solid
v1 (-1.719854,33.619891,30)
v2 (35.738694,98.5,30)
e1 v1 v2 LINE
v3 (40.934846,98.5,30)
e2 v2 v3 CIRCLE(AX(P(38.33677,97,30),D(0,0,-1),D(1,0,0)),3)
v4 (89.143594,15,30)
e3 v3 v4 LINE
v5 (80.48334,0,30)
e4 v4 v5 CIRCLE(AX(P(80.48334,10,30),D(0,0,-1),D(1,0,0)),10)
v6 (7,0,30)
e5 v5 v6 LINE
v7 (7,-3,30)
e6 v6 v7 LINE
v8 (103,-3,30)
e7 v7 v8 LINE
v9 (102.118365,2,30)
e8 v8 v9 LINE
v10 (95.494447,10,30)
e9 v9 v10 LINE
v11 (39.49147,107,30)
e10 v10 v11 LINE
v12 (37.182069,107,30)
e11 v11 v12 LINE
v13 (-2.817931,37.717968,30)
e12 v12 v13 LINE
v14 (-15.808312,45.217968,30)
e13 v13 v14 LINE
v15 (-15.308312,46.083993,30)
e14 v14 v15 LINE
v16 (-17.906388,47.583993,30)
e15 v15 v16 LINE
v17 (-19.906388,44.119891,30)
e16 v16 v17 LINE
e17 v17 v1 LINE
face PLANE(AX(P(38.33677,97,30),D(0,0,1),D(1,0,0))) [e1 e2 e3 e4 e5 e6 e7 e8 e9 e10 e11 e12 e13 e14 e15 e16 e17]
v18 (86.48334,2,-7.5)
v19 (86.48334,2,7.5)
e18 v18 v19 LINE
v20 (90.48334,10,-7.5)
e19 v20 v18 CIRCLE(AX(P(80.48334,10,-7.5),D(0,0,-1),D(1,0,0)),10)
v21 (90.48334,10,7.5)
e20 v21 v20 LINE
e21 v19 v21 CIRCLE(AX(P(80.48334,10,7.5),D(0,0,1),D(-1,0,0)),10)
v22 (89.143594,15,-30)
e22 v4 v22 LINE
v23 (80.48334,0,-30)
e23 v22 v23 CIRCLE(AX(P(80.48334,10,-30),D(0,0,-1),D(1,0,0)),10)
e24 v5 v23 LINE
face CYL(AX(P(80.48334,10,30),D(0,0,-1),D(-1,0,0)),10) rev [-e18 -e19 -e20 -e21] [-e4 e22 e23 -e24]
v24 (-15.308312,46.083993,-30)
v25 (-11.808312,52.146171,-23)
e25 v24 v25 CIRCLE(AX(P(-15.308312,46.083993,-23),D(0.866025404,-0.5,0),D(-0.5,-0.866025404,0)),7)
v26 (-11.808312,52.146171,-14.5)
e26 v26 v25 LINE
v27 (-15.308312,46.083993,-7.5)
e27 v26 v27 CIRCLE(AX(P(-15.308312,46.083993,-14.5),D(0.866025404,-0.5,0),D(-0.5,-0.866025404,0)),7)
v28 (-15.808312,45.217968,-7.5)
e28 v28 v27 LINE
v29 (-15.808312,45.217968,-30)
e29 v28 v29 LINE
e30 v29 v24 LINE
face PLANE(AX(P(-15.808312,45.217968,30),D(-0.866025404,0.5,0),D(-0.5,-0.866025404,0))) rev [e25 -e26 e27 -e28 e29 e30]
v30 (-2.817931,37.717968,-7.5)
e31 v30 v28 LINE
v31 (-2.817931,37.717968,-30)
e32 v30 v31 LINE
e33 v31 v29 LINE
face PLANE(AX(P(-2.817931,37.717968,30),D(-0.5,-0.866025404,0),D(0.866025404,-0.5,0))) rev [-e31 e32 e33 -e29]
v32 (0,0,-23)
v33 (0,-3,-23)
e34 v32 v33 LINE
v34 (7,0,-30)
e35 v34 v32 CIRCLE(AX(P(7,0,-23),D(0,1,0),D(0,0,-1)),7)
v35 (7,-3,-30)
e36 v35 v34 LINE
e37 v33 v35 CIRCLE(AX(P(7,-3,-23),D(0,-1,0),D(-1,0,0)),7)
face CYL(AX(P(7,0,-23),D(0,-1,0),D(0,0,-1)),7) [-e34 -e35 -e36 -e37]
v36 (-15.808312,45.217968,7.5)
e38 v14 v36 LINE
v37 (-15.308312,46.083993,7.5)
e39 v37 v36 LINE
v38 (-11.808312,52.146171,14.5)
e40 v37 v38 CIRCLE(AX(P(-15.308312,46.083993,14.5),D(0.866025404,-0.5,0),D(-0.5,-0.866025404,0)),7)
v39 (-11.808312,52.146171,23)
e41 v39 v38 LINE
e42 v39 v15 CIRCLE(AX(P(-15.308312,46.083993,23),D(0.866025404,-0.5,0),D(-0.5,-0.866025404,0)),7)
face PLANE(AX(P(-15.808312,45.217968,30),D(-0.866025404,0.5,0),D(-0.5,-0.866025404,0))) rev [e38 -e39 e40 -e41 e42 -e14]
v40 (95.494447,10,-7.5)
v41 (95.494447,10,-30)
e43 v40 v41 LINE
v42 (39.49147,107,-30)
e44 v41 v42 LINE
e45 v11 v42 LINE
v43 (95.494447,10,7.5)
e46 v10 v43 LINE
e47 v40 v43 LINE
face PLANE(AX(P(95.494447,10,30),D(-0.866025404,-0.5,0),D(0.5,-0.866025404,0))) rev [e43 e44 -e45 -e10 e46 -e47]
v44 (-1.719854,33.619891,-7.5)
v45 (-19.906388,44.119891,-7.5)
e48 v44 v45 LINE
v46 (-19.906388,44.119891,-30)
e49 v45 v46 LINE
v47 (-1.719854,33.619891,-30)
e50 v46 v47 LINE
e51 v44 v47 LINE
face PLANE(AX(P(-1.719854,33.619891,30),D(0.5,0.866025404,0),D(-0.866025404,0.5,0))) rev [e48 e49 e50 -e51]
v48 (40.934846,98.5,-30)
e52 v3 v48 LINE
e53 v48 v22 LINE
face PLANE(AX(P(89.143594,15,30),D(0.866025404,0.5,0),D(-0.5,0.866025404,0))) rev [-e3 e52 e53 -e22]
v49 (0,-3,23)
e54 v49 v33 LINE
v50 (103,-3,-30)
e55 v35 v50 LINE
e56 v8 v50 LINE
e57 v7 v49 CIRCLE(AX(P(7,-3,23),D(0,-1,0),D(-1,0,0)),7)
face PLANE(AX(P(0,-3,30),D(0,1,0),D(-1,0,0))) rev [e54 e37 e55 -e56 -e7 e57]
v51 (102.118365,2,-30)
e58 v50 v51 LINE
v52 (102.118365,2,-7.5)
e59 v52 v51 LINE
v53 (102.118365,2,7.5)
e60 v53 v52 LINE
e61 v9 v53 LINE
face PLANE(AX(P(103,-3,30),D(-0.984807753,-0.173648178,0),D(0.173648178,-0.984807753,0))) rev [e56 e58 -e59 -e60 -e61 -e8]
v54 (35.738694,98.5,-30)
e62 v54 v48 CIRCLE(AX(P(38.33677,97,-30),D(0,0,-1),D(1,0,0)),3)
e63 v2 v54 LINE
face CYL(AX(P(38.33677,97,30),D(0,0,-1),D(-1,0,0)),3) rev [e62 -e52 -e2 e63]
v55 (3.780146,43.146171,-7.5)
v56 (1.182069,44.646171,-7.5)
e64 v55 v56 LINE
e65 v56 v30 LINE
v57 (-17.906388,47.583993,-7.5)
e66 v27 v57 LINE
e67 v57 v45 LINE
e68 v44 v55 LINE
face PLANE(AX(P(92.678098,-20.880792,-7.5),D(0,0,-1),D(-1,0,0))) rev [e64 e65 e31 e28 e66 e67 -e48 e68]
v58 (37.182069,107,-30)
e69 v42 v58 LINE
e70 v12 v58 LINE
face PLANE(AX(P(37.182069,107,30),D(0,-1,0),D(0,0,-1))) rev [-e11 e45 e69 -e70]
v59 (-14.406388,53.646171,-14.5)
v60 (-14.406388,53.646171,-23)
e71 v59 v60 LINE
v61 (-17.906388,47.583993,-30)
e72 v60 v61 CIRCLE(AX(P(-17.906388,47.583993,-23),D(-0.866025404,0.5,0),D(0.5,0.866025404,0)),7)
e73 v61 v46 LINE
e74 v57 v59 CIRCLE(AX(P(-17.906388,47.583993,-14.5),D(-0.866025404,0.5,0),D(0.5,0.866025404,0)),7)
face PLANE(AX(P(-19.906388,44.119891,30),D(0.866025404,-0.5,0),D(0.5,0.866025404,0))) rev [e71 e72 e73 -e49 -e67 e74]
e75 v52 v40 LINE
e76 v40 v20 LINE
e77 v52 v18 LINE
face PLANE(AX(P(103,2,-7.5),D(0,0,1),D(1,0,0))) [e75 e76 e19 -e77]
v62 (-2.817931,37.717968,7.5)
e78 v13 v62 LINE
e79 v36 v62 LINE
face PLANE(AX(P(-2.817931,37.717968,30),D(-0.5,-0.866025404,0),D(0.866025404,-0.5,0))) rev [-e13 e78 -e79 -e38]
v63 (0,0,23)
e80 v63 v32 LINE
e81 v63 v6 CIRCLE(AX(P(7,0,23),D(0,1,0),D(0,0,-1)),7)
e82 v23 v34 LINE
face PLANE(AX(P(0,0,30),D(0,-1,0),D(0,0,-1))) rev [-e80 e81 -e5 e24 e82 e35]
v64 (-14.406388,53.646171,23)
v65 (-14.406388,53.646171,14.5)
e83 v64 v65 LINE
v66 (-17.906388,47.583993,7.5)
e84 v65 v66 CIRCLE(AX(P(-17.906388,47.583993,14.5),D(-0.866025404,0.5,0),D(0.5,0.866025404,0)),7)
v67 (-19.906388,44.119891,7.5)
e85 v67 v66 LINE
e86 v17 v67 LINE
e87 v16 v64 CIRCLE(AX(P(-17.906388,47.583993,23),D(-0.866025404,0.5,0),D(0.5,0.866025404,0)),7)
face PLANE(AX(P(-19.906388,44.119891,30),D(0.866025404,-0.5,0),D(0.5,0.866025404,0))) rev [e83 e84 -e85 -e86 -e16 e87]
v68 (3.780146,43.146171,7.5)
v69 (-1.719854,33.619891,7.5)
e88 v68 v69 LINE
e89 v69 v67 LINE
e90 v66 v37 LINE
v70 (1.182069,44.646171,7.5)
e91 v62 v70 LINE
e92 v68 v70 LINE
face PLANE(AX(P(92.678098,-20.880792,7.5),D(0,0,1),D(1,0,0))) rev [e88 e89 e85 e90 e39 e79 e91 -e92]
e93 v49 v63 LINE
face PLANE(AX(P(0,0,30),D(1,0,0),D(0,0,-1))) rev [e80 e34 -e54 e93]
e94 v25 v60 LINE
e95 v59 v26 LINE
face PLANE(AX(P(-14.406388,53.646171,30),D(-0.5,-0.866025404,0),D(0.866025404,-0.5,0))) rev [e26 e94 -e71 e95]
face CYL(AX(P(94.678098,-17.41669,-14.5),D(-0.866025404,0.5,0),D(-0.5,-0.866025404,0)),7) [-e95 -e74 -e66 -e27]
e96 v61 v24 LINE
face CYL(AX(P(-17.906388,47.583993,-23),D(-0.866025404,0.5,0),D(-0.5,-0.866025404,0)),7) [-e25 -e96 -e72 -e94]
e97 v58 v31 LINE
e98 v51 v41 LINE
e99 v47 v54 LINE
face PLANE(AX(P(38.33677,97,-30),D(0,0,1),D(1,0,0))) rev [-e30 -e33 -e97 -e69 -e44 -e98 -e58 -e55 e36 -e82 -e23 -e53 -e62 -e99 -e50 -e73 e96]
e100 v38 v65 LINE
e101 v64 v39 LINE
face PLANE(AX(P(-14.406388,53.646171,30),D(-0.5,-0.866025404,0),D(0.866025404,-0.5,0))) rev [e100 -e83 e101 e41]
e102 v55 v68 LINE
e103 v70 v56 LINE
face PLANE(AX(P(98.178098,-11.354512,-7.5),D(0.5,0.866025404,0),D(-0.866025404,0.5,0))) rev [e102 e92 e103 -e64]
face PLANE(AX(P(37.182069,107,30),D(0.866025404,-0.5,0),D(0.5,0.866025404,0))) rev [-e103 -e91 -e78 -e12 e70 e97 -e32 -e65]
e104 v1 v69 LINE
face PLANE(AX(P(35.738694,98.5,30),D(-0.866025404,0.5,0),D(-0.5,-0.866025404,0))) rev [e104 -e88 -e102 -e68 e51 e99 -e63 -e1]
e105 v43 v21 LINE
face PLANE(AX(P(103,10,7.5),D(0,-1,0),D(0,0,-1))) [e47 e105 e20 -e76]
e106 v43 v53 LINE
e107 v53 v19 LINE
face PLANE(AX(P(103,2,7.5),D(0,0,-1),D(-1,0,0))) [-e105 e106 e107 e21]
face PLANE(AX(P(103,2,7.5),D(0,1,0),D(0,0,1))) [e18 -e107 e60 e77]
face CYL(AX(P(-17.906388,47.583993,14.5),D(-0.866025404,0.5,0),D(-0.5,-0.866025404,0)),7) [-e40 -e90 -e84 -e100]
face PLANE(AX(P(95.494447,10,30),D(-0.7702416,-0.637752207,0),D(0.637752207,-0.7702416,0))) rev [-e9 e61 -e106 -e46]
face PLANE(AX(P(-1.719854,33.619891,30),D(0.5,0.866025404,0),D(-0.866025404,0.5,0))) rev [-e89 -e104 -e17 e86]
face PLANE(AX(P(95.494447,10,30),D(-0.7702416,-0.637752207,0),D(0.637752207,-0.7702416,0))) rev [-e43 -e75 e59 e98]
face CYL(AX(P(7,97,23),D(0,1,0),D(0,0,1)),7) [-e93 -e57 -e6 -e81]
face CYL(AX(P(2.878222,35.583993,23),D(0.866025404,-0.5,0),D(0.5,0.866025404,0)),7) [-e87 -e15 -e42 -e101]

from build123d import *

# Parameters (mm, degrees)
STAND_BODY_60MM_DEPTH = 30
CABLE_NOTCH_SKETCH_W  = 15
CABLE_NOTCH_SKETCH_H  = 8
CABLE_NOTCH_DEPTH     = 152.518975709
SLOT_15X11_REACH      = 167.253
SLOT_15X11_SKETCH_W   = 15
SLOT_15X11_SKETCH_H   = 11
SLOT_EDGE_FILLET_R7_R = 7
BEND_FILLET_R7_R      = 7


with BuildPart() as part:
    # Stand Profile Sketch → Stand Body 60mm (new, symmetric)
    with BuildSketch(Plane.XY):
        with BuildLine():
            Line((0, 0), (80.483339502, 0))
            ThreePointArc((80.483339502, 0), (89.143593539, 5), (89.143593539, 15))
            Line((89.143593539, 15), (40.934846062, 98.5))
            ThreePointArc((40.934846062, 98.5), (38.336769851, 100), (35.738693639, 98.5))
            Line((35.738693639, 98.5), (-1.719854476, 33.619891486))
            Line((-1.719854476, 33.619891486), (-19.906387956, 44.119891486))
            Line((-19.906387956, 44.119891486), (-14.406387956, 53.646170928))
            Line((-14.406387956, 53.646170928), (-11.808311744, 52.146170928))
            Line((-11.808311744, 52.146170928), (-15.808311744, 45.217967697))
            Line((-15.808311744, 45.217967697), (-2.817930688, 37.717967697))
            Line((-2.817930688, 37.717967697), (37.182069312, 107))
            Line((37.182069312, 107), (39.491470389, 107))
            Line((39.491470389, 107), (95.494446501, 10))
            Line((95.494446501, 10), (102.118365096, 2))
            Line((102.118365096, 2), (103, -3))
            Line((103, -3), (0, -3))
            Line((0, -3), (0, 0))
        make_face()
    extrude(amount=STAND_BODY_60MM_DEPTH, both=True)

    # Cable Notch Sketch → Cable Notch (cut, through all)
    with BuildSketch(Plane(origin=(0, 0, 0), x_dir=(0, 0, -1), z_dir=(1, 0, 0))):
        with Locations((0, 6)):
            Rectangle(CABLE_NOTCH_SKETCH_W, CABLE_NOTCH_SKETCH_H)
    extrude(amount=CABLE_NOTCH_DEPTH, mode=Mode.SUBTRACT)

    # Slot 15x11 Sketch → Slot 15x11 (cut, up to next)
    with BuildSketch(Plane(origin=(-34.034264386, 19.649691705, 0), x_dir=(0, 0, 1), z_dir=(-0.8660254037844446, 0.49999999999998995, 0)), mode=Mode.PRIVATE) as slot_15x11_sk1:
        with Locations((0, 33.755752861)):
            Rectangle(SLOT_15X11_SKETCH_W, SLOT_15X11_SKETCH_H)
    slot_15x11_tool1 = extrude(slot_15x11_sk1.sketch, amount=-SLOT_15X11_REACH, mode=Mode.PRIVATE) & part.part
    add(slot_15x11_tool1.solids().sort_by_distance((-17.156388, 48.883031, 0))[0], mode=Mode.SUBTRACT)

    # Slot Edge Fillet R7
    slot_edge_fillet_r7_edges = [part.edges().sort_by_distance(p)[0] for p in [
        (-13.10734985, 52.896170928, -30),
        (-13.10734985, 52.896170928, 30),
        (-13.10734985, 52.896170928, 7.5),
        (-13.10734985, 52.896170928, -7.5),
    ]]
    fillet(slot_edge_fillet_r7_edges, radius=SLOT_EDGE_FILLET_R7_R)

    # Bend Fillet R7
    bend_fillet_r7_edges = [part.edges().sort_by_distance(p)[0] for p in [
        (0, -1.5, -30),
        (0, -1.5, 30),
    ]]
    fillet(bend_fillet_r7_edges, radius=BEND_FILLET_R7_R)


solid = part.part
